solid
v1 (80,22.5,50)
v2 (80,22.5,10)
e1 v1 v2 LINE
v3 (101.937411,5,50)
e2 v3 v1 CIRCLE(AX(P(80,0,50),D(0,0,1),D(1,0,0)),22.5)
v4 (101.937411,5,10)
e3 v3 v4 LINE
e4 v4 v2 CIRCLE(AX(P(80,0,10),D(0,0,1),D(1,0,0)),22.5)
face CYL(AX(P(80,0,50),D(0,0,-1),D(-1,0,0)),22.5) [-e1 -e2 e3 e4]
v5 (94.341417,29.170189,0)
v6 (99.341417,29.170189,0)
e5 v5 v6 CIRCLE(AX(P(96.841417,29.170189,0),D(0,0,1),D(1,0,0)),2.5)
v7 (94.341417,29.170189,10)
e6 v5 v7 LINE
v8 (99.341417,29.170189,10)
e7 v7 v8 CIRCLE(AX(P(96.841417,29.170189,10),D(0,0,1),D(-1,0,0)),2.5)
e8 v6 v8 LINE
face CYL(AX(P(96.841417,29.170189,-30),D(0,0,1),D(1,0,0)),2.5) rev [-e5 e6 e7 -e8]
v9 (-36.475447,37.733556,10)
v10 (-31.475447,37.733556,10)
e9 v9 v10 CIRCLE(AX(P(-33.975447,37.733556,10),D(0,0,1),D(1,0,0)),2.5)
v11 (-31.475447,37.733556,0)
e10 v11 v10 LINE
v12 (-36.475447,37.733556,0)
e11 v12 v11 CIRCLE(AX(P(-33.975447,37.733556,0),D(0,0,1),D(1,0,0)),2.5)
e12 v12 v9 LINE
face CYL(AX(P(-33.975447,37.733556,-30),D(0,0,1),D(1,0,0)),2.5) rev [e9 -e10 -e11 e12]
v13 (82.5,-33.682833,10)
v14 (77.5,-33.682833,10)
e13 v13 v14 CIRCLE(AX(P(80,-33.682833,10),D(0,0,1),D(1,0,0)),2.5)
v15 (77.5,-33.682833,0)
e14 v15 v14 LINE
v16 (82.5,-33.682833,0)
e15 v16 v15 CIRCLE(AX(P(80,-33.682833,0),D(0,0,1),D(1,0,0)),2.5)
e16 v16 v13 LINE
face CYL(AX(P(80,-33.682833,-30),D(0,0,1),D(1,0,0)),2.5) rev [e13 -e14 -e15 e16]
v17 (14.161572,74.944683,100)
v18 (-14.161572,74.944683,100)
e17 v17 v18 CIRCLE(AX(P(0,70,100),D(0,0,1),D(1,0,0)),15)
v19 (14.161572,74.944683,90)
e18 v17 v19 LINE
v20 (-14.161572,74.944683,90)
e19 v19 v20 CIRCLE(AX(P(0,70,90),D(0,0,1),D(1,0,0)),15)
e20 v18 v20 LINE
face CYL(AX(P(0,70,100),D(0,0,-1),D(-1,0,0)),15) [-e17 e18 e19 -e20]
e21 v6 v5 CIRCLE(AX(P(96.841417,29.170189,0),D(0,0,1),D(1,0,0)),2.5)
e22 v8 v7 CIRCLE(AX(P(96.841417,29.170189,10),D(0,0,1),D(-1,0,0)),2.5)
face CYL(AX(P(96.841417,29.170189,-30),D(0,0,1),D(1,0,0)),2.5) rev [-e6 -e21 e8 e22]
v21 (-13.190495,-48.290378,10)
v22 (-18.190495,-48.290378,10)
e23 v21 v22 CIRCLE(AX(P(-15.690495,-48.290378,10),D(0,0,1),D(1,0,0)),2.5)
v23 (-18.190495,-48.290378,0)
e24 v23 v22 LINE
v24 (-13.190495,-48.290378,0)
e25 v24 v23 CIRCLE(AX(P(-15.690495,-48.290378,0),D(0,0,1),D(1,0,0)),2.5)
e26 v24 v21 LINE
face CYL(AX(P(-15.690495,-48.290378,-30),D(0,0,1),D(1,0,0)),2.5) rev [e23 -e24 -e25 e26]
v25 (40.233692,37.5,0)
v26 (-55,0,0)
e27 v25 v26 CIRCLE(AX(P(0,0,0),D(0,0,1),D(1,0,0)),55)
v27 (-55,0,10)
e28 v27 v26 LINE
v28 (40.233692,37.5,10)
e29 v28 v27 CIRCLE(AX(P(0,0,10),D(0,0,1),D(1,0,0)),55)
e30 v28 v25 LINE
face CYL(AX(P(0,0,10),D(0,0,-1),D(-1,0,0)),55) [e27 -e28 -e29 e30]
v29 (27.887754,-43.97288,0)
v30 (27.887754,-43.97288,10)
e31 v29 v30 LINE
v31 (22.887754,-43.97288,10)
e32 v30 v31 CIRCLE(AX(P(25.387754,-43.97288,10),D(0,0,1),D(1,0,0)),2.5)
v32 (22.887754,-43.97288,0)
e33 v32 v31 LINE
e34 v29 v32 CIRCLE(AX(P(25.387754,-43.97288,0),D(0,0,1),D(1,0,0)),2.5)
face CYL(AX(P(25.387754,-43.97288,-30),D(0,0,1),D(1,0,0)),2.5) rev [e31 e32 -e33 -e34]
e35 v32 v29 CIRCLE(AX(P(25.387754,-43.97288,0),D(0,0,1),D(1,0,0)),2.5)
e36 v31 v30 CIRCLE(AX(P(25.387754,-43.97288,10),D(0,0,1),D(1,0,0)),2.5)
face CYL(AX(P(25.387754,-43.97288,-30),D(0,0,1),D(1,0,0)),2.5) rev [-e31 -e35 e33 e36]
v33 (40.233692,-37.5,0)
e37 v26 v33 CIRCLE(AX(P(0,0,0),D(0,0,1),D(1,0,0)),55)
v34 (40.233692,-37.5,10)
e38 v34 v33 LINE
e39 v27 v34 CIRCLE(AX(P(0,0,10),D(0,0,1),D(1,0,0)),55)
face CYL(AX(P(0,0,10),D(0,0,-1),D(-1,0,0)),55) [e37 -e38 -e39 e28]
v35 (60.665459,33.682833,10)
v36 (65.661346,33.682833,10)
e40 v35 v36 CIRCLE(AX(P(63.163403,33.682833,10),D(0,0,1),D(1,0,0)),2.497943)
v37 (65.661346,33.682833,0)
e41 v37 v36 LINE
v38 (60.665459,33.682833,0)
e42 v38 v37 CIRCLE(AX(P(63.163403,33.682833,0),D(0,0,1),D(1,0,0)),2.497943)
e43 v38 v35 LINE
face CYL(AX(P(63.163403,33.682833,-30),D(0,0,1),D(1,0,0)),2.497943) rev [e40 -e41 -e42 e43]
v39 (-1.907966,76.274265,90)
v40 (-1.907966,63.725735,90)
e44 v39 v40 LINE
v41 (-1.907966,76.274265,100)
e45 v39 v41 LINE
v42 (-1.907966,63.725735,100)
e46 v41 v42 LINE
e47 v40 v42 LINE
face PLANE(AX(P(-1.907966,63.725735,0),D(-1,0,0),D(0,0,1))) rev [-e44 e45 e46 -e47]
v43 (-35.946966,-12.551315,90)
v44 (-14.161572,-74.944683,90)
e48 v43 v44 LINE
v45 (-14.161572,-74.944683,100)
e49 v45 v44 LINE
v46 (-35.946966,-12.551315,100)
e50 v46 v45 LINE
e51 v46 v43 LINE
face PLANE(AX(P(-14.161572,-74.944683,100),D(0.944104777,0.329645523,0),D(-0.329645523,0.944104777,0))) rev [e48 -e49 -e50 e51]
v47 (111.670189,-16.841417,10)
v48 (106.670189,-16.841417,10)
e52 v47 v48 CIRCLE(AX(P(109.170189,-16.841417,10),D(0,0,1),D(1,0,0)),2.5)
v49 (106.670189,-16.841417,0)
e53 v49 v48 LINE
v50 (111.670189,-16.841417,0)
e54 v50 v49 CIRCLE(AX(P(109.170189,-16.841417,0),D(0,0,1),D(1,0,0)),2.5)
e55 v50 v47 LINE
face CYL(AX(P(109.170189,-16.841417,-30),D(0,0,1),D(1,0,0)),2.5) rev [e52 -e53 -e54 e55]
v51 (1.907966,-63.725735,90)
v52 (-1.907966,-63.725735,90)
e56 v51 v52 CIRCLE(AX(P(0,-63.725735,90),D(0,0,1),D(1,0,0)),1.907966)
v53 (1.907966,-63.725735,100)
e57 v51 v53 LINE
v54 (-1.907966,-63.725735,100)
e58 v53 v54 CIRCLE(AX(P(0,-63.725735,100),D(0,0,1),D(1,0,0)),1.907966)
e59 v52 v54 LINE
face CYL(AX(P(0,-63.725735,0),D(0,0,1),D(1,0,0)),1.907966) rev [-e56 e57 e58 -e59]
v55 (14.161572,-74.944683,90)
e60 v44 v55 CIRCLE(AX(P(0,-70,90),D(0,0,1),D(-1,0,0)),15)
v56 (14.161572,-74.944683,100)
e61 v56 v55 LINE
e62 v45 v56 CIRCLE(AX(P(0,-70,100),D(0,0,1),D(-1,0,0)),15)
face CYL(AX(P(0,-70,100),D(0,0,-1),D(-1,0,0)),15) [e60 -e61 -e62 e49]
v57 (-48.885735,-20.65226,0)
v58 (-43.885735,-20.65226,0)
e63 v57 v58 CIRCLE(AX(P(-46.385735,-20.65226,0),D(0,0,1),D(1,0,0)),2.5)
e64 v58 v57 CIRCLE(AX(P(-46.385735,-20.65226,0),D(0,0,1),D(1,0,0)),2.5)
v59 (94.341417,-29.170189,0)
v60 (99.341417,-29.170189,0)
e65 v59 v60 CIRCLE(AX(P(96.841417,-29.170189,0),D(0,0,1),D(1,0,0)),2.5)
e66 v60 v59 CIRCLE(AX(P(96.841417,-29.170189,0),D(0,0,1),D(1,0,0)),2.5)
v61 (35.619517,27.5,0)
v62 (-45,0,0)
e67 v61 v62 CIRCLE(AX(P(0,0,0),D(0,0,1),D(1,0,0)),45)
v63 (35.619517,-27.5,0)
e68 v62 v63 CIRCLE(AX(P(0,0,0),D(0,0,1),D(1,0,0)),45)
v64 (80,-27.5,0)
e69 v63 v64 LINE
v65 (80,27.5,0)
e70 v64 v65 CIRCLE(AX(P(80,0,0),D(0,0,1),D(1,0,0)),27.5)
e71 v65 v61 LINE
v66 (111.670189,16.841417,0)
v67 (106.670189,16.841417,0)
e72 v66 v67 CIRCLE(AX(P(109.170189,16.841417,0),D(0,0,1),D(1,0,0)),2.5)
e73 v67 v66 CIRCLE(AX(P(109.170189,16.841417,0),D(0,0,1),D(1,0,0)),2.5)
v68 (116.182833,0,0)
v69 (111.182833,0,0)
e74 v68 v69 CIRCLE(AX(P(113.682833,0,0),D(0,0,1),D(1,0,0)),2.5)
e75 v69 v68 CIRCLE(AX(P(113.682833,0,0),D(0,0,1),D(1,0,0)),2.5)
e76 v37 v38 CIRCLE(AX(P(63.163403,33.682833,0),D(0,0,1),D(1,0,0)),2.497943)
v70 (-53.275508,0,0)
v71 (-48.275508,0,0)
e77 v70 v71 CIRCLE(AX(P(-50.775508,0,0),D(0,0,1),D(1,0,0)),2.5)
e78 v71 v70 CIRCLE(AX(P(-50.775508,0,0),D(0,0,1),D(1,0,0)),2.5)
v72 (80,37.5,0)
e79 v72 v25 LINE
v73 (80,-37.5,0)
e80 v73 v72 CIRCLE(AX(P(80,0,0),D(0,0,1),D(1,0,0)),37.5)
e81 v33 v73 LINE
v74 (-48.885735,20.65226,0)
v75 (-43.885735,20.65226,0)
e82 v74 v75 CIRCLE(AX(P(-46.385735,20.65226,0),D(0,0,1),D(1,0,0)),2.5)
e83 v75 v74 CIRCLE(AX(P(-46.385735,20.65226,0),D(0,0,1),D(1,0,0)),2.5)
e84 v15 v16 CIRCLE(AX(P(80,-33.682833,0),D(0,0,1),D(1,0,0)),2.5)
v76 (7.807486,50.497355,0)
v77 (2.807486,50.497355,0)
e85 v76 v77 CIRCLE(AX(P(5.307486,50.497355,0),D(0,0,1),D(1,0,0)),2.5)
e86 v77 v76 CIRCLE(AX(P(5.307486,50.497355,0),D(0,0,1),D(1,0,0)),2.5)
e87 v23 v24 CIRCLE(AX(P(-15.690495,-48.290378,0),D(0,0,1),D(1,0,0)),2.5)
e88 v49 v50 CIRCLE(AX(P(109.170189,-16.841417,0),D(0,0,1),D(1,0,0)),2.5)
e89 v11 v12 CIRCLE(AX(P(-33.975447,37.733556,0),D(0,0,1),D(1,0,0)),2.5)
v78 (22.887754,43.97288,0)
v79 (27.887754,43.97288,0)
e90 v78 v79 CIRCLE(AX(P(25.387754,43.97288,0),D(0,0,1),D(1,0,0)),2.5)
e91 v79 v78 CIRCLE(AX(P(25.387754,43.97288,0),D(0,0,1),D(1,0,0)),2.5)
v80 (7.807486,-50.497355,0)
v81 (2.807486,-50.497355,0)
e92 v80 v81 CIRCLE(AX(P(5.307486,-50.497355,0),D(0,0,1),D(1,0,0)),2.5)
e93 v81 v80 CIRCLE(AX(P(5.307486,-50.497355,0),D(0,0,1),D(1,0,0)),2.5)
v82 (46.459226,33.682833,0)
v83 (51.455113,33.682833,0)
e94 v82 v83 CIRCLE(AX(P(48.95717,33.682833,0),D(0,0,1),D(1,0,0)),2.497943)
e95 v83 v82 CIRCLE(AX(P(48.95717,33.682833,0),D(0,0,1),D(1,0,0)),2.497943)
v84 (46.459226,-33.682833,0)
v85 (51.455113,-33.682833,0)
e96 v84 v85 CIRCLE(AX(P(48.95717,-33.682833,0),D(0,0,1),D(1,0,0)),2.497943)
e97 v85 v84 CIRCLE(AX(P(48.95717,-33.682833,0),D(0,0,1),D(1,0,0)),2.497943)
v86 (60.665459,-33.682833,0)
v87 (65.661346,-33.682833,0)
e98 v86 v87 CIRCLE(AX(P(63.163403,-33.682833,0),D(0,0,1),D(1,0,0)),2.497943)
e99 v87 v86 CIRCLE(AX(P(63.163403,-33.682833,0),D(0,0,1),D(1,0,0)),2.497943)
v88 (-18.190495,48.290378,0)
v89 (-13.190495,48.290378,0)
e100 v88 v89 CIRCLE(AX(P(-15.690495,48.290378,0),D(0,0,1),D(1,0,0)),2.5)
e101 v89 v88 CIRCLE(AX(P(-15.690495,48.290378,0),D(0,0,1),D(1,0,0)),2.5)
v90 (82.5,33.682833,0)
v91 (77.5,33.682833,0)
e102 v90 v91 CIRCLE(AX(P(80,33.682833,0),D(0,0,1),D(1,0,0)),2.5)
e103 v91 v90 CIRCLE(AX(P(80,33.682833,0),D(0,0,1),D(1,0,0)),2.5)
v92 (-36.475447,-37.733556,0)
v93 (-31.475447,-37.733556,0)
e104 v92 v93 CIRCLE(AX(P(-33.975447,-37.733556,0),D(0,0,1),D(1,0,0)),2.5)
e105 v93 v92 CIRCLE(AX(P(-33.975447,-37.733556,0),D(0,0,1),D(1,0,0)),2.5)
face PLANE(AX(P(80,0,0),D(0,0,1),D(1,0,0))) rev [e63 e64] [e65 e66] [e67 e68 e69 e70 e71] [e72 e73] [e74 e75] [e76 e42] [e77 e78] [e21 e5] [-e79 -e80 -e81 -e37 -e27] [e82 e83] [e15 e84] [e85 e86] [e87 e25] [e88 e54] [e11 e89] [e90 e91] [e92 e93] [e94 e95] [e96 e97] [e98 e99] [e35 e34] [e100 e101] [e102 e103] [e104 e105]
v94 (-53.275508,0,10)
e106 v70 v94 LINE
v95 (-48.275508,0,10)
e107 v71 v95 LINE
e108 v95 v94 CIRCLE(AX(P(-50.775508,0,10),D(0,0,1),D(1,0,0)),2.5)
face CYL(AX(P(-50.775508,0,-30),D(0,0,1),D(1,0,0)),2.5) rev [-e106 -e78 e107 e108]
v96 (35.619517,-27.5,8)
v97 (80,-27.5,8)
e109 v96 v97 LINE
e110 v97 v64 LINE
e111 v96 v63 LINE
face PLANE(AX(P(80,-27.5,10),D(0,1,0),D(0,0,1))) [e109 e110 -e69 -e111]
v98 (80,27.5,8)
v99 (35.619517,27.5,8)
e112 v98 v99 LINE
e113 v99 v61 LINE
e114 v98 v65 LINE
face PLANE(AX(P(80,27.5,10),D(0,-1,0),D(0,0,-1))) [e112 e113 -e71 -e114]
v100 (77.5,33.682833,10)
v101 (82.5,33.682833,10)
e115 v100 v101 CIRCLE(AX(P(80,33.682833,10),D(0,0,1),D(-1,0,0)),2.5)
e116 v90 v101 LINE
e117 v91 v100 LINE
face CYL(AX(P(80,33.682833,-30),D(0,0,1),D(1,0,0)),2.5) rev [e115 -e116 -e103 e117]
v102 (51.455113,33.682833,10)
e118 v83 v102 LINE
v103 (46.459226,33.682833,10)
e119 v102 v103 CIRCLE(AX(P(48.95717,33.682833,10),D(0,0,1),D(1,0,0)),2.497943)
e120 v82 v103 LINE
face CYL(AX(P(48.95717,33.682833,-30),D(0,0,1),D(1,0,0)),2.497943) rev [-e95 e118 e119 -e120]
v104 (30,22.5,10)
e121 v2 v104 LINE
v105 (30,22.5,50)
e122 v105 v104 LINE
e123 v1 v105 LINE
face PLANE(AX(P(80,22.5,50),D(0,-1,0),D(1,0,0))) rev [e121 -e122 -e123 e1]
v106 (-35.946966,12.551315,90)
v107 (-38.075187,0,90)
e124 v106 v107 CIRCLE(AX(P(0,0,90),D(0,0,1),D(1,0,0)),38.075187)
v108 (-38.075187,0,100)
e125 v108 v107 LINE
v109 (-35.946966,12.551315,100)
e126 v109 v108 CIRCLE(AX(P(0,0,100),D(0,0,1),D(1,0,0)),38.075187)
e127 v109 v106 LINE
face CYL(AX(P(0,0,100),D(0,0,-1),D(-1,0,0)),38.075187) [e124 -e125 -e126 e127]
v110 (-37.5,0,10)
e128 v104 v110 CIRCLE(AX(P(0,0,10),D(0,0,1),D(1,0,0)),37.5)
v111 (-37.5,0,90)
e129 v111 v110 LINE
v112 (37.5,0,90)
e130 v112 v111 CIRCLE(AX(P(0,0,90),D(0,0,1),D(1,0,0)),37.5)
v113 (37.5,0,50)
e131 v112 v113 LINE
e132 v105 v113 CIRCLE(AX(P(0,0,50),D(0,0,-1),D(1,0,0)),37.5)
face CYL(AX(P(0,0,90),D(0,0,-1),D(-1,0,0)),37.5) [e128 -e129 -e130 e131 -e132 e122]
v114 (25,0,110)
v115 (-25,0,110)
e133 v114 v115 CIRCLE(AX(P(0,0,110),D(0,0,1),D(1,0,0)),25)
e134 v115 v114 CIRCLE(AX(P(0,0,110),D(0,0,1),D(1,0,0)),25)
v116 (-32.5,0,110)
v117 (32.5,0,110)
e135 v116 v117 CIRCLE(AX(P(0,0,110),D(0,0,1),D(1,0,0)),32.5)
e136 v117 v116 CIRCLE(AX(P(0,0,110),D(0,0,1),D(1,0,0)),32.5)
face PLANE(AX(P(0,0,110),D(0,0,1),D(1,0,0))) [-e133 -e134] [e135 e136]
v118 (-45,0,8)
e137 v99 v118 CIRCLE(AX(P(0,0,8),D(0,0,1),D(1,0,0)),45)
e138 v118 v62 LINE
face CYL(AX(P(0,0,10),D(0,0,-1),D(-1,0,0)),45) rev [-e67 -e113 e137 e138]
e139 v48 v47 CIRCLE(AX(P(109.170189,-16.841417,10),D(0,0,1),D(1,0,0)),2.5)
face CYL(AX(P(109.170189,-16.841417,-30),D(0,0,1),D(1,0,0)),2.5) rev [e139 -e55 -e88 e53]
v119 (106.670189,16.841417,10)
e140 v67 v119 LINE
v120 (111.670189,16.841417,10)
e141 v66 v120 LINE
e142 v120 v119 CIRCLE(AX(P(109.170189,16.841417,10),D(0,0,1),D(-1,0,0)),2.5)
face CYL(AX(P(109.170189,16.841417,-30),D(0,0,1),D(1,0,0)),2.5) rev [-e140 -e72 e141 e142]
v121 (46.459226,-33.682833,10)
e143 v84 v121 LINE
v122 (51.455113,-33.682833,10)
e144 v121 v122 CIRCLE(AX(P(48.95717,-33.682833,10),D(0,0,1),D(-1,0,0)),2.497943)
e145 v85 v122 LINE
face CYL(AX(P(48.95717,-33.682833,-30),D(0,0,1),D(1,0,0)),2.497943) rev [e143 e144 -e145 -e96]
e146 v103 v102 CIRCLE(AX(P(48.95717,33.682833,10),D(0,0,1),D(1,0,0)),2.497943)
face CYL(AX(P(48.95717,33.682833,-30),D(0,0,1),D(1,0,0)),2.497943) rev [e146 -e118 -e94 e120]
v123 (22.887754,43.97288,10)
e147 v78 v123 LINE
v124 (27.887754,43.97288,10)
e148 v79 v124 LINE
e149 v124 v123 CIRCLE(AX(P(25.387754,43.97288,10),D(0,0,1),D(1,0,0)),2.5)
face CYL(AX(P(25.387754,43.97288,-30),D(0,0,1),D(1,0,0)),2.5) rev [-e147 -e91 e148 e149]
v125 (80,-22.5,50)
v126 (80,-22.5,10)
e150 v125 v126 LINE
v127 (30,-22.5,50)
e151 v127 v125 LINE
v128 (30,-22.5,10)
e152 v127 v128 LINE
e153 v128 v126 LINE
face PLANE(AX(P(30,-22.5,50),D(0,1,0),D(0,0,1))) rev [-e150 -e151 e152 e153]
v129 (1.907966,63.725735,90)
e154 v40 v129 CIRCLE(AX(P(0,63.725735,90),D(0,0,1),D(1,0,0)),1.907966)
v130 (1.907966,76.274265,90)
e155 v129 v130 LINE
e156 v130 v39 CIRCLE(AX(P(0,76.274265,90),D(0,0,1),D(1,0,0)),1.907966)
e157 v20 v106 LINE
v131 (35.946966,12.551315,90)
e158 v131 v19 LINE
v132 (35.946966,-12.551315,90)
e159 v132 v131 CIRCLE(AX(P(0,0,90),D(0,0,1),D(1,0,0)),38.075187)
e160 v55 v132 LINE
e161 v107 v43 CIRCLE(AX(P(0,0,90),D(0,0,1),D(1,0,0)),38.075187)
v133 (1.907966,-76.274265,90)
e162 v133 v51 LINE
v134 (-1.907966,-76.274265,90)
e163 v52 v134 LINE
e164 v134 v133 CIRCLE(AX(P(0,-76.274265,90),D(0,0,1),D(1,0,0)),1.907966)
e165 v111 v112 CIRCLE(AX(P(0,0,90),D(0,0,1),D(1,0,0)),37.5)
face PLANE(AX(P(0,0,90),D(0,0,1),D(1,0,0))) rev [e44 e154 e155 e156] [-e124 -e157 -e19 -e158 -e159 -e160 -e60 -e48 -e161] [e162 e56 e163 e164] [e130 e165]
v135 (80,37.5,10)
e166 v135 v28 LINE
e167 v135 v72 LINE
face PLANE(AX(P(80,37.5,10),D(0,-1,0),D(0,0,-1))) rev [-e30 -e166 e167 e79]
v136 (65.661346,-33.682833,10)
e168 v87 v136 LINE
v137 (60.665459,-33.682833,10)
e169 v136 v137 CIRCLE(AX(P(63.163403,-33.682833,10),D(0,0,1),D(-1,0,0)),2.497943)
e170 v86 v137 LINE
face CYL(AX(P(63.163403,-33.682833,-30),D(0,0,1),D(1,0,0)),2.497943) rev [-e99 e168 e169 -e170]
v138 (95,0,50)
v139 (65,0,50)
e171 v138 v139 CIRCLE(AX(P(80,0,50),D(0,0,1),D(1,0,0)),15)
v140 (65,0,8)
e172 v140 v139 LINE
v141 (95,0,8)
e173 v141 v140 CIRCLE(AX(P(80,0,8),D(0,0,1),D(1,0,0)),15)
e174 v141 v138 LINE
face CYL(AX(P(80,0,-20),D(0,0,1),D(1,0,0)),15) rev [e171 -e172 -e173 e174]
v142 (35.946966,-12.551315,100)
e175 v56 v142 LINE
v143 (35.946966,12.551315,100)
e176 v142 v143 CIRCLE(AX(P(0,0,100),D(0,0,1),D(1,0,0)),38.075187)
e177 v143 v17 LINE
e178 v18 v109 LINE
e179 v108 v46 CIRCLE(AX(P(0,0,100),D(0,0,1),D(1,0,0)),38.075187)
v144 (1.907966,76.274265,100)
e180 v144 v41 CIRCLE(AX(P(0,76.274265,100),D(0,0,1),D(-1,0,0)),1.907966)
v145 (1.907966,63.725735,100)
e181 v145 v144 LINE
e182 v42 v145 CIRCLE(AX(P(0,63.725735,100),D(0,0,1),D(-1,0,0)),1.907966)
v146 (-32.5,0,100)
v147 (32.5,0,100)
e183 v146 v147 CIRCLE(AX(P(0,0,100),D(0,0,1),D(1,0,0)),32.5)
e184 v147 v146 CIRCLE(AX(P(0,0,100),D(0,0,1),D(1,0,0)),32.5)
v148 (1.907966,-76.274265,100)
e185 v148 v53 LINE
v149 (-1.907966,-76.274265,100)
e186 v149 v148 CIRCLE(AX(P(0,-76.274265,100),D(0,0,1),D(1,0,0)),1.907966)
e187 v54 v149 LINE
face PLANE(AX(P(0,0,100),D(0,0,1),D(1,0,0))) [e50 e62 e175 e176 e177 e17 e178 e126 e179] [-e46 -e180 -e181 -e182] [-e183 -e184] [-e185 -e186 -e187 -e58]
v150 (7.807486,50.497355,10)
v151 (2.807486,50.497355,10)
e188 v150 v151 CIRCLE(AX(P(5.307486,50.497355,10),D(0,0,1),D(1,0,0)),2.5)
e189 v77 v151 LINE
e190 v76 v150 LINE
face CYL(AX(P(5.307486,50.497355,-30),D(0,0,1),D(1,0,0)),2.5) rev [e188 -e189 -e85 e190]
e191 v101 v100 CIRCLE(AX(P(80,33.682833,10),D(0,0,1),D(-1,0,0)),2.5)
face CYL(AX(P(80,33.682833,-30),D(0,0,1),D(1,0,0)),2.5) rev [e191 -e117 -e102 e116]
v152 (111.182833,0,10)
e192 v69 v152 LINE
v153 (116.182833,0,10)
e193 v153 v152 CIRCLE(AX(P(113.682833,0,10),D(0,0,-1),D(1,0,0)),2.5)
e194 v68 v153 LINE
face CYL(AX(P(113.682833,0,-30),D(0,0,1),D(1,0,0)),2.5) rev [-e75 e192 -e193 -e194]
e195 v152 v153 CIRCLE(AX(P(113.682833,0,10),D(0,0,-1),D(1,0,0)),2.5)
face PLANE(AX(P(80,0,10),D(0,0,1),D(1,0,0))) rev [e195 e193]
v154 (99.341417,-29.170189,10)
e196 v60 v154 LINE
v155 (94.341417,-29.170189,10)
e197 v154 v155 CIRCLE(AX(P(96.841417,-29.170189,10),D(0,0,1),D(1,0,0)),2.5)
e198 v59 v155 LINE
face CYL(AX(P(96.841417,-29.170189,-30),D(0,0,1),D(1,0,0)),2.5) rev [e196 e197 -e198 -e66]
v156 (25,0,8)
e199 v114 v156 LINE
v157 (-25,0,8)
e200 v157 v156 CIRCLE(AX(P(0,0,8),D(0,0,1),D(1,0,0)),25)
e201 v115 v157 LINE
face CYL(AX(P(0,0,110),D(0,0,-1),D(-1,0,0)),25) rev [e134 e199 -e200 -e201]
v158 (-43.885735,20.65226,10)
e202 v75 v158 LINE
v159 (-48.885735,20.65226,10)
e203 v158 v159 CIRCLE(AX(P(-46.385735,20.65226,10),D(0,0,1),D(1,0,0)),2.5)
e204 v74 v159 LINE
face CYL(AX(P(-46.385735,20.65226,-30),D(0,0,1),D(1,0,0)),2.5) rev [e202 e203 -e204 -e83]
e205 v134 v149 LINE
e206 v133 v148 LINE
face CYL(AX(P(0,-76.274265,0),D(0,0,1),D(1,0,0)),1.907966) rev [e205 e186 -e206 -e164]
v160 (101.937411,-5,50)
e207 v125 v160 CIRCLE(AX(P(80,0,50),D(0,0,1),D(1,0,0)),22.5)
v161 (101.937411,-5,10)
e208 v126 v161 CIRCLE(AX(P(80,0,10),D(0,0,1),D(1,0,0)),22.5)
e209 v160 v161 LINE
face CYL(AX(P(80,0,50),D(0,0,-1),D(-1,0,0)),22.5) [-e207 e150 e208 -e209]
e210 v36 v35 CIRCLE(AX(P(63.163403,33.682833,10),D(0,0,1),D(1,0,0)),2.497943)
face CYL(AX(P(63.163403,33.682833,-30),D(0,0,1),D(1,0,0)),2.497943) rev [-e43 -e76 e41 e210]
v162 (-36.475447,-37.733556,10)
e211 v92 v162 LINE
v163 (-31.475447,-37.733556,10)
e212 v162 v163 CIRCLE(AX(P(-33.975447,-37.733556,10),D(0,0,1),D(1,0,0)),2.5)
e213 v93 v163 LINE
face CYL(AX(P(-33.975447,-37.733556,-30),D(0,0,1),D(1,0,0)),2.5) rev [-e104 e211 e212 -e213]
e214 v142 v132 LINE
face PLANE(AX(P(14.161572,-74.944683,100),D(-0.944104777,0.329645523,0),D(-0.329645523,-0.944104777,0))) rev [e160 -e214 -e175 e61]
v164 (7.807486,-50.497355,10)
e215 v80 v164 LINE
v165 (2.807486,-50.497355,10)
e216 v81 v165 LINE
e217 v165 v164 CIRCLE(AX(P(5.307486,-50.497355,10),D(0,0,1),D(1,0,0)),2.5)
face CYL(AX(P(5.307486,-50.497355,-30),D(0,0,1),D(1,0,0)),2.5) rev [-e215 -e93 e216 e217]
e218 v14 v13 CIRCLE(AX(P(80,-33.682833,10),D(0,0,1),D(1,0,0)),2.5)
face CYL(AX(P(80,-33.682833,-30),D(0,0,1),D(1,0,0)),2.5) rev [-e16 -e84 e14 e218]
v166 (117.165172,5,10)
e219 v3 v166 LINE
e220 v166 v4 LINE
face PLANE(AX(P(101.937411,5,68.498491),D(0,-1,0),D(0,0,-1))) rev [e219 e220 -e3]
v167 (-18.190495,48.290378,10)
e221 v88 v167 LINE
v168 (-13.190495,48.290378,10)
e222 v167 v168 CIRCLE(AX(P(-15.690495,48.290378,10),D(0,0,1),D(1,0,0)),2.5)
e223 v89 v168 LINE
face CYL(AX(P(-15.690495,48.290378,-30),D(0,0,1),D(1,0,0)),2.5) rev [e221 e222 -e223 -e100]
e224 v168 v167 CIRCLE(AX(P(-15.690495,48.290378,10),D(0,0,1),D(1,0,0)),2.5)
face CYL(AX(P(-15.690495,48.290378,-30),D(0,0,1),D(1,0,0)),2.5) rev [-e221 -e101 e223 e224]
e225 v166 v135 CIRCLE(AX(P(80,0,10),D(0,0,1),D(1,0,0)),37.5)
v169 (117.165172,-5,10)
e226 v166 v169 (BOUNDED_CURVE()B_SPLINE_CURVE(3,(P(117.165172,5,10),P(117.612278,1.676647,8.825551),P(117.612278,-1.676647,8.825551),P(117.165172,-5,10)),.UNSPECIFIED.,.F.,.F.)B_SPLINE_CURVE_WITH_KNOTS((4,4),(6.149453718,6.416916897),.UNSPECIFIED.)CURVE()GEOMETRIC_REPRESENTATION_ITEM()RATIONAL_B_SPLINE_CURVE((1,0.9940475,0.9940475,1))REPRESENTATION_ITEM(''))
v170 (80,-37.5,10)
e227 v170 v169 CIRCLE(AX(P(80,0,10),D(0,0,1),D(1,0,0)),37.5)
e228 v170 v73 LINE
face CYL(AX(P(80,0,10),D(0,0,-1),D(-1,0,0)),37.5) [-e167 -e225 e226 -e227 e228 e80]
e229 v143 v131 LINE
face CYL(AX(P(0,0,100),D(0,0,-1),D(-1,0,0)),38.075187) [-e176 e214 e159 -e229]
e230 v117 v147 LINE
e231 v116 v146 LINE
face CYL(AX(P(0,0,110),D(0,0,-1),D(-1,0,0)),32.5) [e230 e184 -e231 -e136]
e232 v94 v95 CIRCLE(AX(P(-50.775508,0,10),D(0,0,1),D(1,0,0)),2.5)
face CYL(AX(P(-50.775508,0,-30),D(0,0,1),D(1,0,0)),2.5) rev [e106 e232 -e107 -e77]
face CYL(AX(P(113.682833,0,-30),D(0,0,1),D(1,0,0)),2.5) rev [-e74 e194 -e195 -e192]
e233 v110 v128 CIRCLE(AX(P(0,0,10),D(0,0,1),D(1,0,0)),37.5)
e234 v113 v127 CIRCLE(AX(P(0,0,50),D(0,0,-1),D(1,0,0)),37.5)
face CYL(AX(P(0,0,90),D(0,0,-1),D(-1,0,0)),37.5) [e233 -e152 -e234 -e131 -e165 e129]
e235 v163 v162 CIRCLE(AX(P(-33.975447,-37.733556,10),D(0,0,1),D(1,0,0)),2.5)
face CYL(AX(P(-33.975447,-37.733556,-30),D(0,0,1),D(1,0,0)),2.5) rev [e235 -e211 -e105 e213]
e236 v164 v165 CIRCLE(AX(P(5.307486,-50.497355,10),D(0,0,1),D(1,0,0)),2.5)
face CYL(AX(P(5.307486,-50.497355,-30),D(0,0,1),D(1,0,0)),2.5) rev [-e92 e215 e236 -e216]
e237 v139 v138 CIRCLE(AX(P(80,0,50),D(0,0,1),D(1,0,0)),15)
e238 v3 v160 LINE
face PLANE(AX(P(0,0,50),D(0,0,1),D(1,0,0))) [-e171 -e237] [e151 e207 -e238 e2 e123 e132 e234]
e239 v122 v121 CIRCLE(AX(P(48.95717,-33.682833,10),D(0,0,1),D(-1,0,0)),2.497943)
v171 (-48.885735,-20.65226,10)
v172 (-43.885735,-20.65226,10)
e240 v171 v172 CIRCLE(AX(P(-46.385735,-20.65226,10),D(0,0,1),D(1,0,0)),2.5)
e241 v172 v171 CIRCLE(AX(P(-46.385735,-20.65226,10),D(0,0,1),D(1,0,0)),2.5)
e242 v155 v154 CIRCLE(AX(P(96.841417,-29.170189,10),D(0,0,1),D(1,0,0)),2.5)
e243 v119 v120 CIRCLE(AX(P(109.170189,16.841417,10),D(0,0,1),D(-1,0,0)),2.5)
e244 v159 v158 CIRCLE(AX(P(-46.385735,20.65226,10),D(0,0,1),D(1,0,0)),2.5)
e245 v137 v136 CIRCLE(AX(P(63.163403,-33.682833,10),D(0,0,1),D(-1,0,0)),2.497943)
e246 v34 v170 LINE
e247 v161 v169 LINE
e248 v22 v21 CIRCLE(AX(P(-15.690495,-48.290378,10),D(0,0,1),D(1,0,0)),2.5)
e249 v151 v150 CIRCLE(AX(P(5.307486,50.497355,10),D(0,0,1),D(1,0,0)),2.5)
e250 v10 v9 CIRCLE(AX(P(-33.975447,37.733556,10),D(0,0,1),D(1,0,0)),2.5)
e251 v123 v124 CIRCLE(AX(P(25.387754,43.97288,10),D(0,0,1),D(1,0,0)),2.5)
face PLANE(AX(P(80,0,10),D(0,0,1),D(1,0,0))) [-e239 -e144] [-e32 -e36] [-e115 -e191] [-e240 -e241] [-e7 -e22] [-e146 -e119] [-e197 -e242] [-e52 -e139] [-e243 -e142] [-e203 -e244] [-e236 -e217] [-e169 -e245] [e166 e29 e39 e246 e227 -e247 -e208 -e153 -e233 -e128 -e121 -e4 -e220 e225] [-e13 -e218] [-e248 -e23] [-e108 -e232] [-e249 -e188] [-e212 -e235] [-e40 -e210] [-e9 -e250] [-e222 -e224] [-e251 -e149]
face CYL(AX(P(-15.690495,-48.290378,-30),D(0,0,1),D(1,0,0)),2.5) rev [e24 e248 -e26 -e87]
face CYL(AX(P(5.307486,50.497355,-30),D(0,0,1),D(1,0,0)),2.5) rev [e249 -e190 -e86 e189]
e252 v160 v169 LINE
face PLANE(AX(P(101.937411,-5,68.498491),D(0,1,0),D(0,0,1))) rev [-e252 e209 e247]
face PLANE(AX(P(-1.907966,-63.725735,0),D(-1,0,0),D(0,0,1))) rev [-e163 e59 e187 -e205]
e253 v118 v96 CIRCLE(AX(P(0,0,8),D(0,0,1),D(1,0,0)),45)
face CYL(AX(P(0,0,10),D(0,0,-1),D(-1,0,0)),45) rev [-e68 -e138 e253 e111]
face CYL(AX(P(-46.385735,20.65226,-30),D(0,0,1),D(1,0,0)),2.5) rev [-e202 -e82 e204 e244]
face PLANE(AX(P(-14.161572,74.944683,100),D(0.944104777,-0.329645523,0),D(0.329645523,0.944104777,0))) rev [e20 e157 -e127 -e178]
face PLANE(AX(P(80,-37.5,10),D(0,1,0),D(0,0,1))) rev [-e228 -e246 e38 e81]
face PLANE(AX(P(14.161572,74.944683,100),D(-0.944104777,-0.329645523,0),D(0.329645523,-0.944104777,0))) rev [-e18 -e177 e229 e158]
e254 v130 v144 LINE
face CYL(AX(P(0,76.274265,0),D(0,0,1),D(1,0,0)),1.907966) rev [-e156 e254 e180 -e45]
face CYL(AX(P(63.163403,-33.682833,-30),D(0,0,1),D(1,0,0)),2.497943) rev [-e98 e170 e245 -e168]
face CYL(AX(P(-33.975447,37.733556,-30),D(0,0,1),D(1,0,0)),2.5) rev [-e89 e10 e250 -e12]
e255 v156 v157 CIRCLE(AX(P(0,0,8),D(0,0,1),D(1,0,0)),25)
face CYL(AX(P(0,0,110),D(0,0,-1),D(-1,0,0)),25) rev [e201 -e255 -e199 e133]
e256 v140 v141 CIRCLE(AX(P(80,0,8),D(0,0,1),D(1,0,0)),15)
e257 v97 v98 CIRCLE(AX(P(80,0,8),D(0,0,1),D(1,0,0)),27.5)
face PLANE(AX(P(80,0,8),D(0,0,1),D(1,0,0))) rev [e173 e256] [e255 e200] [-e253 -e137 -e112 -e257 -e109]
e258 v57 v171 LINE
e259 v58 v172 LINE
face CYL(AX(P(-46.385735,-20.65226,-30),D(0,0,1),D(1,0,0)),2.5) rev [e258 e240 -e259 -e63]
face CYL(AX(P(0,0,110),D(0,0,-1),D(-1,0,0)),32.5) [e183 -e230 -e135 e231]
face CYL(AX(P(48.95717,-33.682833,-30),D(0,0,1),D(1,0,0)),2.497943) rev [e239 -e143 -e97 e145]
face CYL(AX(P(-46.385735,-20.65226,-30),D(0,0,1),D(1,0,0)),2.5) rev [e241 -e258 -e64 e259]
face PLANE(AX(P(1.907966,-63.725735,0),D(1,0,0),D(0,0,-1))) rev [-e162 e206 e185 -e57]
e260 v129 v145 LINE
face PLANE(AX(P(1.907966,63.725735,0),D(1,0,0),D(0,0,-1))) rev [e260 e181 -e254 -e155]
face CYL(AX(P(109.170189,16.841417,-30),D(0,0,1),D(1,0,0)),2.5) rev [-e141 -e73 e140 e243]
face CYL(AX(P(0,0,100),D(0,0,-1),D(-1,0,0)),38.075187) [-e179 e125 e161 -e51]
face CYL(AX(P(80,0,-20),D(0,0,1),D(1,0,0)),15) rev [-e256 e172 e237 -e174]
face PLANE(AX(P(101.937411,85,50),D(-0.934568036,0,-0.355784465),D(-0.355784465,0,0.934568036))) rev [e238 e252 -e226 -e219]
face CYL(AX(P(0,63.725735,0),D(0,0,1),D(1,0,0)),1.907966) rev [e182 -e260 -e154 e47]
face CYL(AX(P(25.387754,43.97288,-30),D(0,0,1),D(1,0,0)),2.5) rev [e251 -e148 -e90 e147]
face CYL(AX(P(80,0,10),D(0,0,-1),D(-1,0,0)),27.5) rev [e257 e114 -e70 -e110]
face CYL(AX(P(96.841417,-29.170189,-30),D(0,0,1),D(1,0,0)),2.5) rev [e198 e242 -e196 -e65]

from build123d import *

# Parameters (mm, degrees)
MOUNTING_PLATE_DEPTH       = 10
BARREL_SKETCH_75_R         = 37.5
BARREL_75_DEPTH            = 80
RAISED_START               = -2
RAISED_PAD_2MM_DEPTH       = 2
END_FLANGE_DEPTH           = 10
COLLAR_AND_BORE_SKETCH_R   = 32.5
COLLAR_AND_BORE_SKETCH_R_2 = 25
BORE_COLLAR_65_DEPTH       = 10
SKETCH6_2_R                = 25
MAIN_BORE_50_DEPTH         = 177.1568903
SIDE_ARM_DEPTH             = 40
BOLT_HOLES_SKETCH_R        = 2.497943494
BOLT_HOLES_SKETCH_R_2      = 2.5
PLATE_BOLT_HOLES_DEPTH     = 40
SIDE_BORE_SKETCH_30_R      = 15
SIDE_ARM_BORE_30_DEPTH     = 70
SUPPORT_RIB_DEPTH          = 40
RIB_TRIM_CUT_DEPTH         = 185.407836059
END_FLANGE_SLOTS_DEPTH     = 177.1568903


with BuildPart() as part:
    # Mounting Plate Sketch → Mounting Plate (new body)
    with BuildSketch(Plane.XY):
        with BuildLine():
            Line((80, 37.5), (40.233692349, 37.5))
            ThreePointArc((40.233692349, 37.5), (-55, 0), (40.233692349, -37.5))
            Line((40.233692349, -37.5), (80, -37.5))
            ThreePointArc((80, -37.5), (117.5, 0), (80, 37.5))
        make_face()
        with BuildLine():
            Line((80, -27.5), (35.619517122, -27.5))
            ThreePointArc((35.619517122, -27.5), (-45, 0), (35.619517122, 27.5))
            Line((35.619517122, 27.5), (80, 27.5))
            ThreePointArc((80, 27.5), (107.5, 0), (80, -27.5))
        make_face(mode=Mode.SUBTRACT)
    extrude(amount=MOUNTING_PLATE_DEPTH)



with BuildPart() as body_2:
    # Barrel Sketch _75 → Barrel _75 (new body)
    with BuildSketch(Plane.XY.offset(10)):
        Circle(BARREL_SKETCH_75_R)
    extrude(amount=BARREL_75_DEPTH)


with BuildPart() as part_1:
    add(part.part)

    add(body_2.part)  # Raised Pad 2mm merges body 2
    # Raised Pad Sketch → Raised Pad 2mm (add)
    with BuildSketch(Plane.XY.offset(10).offset(RAISED_START)):
        with BuildLine():
            Line((35.619517122, -27.5), (80, -27.5))
            ThreePointArc((80, -27.5), (107.5, 0), (80, 27.5))
            Line((80, 27.5), (35.619517122, 27.5))
            ThreePointArc((35.619517122, 27.5), (-45, 0), (35.619517122, -27.5))
        make_face()
    extrude(amount=RAISED_PAD_2MM_DEPTH)

    # End Flange Sketch → End Flange (add)
    with BuildSketch(Plane.XY.offset(90)):
        with BuildLine():
            Line((-14.161571651, 74.944682839), (-35.946965527, 12.551314779))
            ThreePointArc((-35.946965527, 12.551314779), (-38.075186582, 0), (-35.946965527, -12.551314779))
            Line((-35.946965527, -12.551314779), (-14.161571651, -74.944682839))
            ThreePointArc((-14.161571651, -74.944682839), (0, -85), (14.161571651, -74.944682839))
            Line((14.161571651, -74.944682839), (35.946965527, -12.551314779))
            ThreePointArc((35.946965527, -12.551314779), (38.075186582, 0), (35.946965527, 12.551314779))
            Line((35.946965527, 12.551314779), (14.161571651, 74.944682839))
            ThreePointArc((14.161571651, 74.944682839), (0, 85), (-14.161571651, 74.944682839))
        make_face()
    extrude(amount=END_FLANGE_DEPTH)

    # Collar And Bore Sketch → Bore Collar _65 (add)
    with BuildSketch(Plane.XY.offset(100)):
        Circle(COLLAR_AND_BORE_SKETCH_R)
        Circle(COLLAR_AND_BORE_SKETCH_R_2, mode=Mode.SUBTRACT)
    extrude(amount=BORE_COLLAR_65_DEPTH)

    # Sketch6_2 → Main Bore _50 (cut, through all)
    with BuildSketch(Plane.XY.offset(100)):
        Circle(SKETCH6_2_R)
    extrude(amount=-MAIN_BORE_50_DEPTH, mode=Mode.SUBTRACT)

    # Side Arm Sketch → Side Arm (add)
    with BuildSketch(Plane.XY.offset(10)):
        with BuildLine():
            Line((80, 22.5), (30, 22.5))
            ThreePointArc((30, 22.5), (37.5, 0), (30, -22.5))
            Line((30, -22.5), (80, -22.5))
            ThreePointArc((80, -22.5), (102.5, 0), (80, 22.5))
        make_face()
    extrude(amount=SIDE_ARM_DEPTH)

    # Bolt Holes Sketch → Plate Bolt Holes (cut)
    with BuildSketch(Plane.XY.offset(10)):
        with Locations((63.163402703, 33.682833364)):
            Circle(BOLT_HOLES_SKETCH_R)
        with Locations((113.682833364, 0)):
            Circle(BOLT_HOLES_SKETCH_R_2)
        with Locations((109.170189364, -16.841416682)):
            Circle(BOLT_HOLES_SKETCH_R_2)
        with Locations((96.841416682, -29.170189364)):
            Circle(BOLT_HOLES_SKETCH_R_2)
        with Locations((80, -33.682833364)):
            Circle(BOLT_HOLES_SKETCH_R_2)
        with Locations((109.170189364, 16.841416682)):
            Circle(BOLT_HOLES_SKETCH_R_2)
        with Locations((80, 33.682833364)):
            Circle(BOLT_HOLES_SKETCH_R_2)
        with Locations((96.841416682, 29.170189364)):
            Circle(BOLT_HOLES_SKETCH_R_2)
        with Locations((-50.775508212, 0)):
            Circle(BOLT_HOLES_SKETCH_R_2)
        with Locations((-46.385734886, 20.652259761)):
            Circle(BOLT_HOLES_SKETCH_R_2)
        with Locations((-33.975446598, 37.733556189)):
            Circle(BOLT_HOLES_SKETCH_R_2)
        with Locations((-15.690494935, 48.290377953)):
            Circle(BOLT_HOLES_SKETCH_R_2)
        with Locations((5.307485845, 50.497354665)):
            Circle(BOLT_HOLES_SKETCH_R_2)
        with Locations((25.387754106, 43.972880001)):
            Circle(BOLT_HOLES_SKETCH_R_2)
        with Locations((25.387754106, -43.972880001)):
            Circle(BOLT_HOLES_SKETCH_R_2)
        with Locations((5.307485845, -50.497354665)):
            Circle(BOLT_HOLES_SKETCH_R_2)
        with Locations((-15.690494935, -48.290377953)):
            Circle(BOLT_HOLES_SKETCH_R_2)
        with Locations((-33.975446598, -37.733556189)):
            Circle(BOLT_HOLES_SKETCH_R_2)
        with Locations((-46.385734886, -20.652259761)):
            Circle(BOLT_HOLES_SKETCH_R_2)
        with Locations((48.957169928, 33.682833364)):
            Circle(BOLT_HOLES_SKETCH_R)
        with Locations((63.163402703, -33.682833364)):
            Circle(BOLT_HOLES_SKETCH_R)
        with Locations((48.957169928, -33.682833364)):
            Circle(BOLT_HOLES_SKETCH_R)
    extrude(amount=-PLATE_BOLT_HOLES_DEPTH, mode=Mode.SUBTRACT)

    # Side Bore Sketch _30 → Side Arm Bore _30 (cut)
    with BuildSketch(Plane.XY.offset(50)):
        with Locations((80, 0)):
            Circle(SIDE_BORE_SKETCH_30_R)
    extrude(amount=-SIDE_ARM_BORE_30_DEPTH, mode=Mode.SUBTRACT)

    # Support Rib Sketch → Support Rib (add)
    with BuildSketch(Plane.XY.offset(10)):
        with BuildLine():
            Line((101.937410968, -5), (117.165171868, -5))
            ThreePointArc((117.165171868, -5), (117.5, 0), (117.165171868, 5))
            Line((117.165171868, 5), (101.937410968, 5))
            ThreePointArc((101.937410968, 5), (102.5, 0), (101.937410968, -5))
        make_face()
    extrude(amount=SUPPORT_RIB_DEPTH)

    # Rib Trim Sketch → Rib Trim Cut (cut, through all)
    with BuildSketch(Plane.XZ.offset(5)):
        Polygon((101.937410968, 50), (130.228414001, -24.314282233), (130.228414001, 50), align=None)
    extrude(amount=-RIB_TRIM_CUT_DEPTH, mode=Mode.SUBTRACT)

    # Flange Slots Sketch → End Flange Slots (cut, through all)
    with BuildSketch(Plane.XY.offset(100)):
        with BuildLine():
            Line((1.907965824, -63.725735382), (1.907965824, -76.274264618))
            ThreePointArc((1.907965824, -76.274264618), (0, -78.182230442), (-1.907965824, -76.274264618))
            Line((-1.907965824, -76.274264618), (-1.907965824, -63.725735382))
            ThreePointArc((-1.907965824, -63.725735382), (0, -61.817769558), (1.907965824, -63.725735382))
        make_face()
        with BuildLine():
            Line((1.907965824, 63.725735382), (1.907965824, 76.274264618))
            ThreePointArc((1.907965824, 76.274264618), (0, 78.182230442), (-1.907965824, 76.274264618))
            Line((-1.907965824, 76.274264618), (-1.907965824, 63.725735382))
            ThreePointArc((-1.907965824, 63.725735382), (0, 61.817769558), (1.907965824, 63.725735382))
        make_face()
    extrude(amount=-END_FLANGE_SLOTS_DEPTH, mode=Mode.SUBTRACT)


solid = part_1.part
